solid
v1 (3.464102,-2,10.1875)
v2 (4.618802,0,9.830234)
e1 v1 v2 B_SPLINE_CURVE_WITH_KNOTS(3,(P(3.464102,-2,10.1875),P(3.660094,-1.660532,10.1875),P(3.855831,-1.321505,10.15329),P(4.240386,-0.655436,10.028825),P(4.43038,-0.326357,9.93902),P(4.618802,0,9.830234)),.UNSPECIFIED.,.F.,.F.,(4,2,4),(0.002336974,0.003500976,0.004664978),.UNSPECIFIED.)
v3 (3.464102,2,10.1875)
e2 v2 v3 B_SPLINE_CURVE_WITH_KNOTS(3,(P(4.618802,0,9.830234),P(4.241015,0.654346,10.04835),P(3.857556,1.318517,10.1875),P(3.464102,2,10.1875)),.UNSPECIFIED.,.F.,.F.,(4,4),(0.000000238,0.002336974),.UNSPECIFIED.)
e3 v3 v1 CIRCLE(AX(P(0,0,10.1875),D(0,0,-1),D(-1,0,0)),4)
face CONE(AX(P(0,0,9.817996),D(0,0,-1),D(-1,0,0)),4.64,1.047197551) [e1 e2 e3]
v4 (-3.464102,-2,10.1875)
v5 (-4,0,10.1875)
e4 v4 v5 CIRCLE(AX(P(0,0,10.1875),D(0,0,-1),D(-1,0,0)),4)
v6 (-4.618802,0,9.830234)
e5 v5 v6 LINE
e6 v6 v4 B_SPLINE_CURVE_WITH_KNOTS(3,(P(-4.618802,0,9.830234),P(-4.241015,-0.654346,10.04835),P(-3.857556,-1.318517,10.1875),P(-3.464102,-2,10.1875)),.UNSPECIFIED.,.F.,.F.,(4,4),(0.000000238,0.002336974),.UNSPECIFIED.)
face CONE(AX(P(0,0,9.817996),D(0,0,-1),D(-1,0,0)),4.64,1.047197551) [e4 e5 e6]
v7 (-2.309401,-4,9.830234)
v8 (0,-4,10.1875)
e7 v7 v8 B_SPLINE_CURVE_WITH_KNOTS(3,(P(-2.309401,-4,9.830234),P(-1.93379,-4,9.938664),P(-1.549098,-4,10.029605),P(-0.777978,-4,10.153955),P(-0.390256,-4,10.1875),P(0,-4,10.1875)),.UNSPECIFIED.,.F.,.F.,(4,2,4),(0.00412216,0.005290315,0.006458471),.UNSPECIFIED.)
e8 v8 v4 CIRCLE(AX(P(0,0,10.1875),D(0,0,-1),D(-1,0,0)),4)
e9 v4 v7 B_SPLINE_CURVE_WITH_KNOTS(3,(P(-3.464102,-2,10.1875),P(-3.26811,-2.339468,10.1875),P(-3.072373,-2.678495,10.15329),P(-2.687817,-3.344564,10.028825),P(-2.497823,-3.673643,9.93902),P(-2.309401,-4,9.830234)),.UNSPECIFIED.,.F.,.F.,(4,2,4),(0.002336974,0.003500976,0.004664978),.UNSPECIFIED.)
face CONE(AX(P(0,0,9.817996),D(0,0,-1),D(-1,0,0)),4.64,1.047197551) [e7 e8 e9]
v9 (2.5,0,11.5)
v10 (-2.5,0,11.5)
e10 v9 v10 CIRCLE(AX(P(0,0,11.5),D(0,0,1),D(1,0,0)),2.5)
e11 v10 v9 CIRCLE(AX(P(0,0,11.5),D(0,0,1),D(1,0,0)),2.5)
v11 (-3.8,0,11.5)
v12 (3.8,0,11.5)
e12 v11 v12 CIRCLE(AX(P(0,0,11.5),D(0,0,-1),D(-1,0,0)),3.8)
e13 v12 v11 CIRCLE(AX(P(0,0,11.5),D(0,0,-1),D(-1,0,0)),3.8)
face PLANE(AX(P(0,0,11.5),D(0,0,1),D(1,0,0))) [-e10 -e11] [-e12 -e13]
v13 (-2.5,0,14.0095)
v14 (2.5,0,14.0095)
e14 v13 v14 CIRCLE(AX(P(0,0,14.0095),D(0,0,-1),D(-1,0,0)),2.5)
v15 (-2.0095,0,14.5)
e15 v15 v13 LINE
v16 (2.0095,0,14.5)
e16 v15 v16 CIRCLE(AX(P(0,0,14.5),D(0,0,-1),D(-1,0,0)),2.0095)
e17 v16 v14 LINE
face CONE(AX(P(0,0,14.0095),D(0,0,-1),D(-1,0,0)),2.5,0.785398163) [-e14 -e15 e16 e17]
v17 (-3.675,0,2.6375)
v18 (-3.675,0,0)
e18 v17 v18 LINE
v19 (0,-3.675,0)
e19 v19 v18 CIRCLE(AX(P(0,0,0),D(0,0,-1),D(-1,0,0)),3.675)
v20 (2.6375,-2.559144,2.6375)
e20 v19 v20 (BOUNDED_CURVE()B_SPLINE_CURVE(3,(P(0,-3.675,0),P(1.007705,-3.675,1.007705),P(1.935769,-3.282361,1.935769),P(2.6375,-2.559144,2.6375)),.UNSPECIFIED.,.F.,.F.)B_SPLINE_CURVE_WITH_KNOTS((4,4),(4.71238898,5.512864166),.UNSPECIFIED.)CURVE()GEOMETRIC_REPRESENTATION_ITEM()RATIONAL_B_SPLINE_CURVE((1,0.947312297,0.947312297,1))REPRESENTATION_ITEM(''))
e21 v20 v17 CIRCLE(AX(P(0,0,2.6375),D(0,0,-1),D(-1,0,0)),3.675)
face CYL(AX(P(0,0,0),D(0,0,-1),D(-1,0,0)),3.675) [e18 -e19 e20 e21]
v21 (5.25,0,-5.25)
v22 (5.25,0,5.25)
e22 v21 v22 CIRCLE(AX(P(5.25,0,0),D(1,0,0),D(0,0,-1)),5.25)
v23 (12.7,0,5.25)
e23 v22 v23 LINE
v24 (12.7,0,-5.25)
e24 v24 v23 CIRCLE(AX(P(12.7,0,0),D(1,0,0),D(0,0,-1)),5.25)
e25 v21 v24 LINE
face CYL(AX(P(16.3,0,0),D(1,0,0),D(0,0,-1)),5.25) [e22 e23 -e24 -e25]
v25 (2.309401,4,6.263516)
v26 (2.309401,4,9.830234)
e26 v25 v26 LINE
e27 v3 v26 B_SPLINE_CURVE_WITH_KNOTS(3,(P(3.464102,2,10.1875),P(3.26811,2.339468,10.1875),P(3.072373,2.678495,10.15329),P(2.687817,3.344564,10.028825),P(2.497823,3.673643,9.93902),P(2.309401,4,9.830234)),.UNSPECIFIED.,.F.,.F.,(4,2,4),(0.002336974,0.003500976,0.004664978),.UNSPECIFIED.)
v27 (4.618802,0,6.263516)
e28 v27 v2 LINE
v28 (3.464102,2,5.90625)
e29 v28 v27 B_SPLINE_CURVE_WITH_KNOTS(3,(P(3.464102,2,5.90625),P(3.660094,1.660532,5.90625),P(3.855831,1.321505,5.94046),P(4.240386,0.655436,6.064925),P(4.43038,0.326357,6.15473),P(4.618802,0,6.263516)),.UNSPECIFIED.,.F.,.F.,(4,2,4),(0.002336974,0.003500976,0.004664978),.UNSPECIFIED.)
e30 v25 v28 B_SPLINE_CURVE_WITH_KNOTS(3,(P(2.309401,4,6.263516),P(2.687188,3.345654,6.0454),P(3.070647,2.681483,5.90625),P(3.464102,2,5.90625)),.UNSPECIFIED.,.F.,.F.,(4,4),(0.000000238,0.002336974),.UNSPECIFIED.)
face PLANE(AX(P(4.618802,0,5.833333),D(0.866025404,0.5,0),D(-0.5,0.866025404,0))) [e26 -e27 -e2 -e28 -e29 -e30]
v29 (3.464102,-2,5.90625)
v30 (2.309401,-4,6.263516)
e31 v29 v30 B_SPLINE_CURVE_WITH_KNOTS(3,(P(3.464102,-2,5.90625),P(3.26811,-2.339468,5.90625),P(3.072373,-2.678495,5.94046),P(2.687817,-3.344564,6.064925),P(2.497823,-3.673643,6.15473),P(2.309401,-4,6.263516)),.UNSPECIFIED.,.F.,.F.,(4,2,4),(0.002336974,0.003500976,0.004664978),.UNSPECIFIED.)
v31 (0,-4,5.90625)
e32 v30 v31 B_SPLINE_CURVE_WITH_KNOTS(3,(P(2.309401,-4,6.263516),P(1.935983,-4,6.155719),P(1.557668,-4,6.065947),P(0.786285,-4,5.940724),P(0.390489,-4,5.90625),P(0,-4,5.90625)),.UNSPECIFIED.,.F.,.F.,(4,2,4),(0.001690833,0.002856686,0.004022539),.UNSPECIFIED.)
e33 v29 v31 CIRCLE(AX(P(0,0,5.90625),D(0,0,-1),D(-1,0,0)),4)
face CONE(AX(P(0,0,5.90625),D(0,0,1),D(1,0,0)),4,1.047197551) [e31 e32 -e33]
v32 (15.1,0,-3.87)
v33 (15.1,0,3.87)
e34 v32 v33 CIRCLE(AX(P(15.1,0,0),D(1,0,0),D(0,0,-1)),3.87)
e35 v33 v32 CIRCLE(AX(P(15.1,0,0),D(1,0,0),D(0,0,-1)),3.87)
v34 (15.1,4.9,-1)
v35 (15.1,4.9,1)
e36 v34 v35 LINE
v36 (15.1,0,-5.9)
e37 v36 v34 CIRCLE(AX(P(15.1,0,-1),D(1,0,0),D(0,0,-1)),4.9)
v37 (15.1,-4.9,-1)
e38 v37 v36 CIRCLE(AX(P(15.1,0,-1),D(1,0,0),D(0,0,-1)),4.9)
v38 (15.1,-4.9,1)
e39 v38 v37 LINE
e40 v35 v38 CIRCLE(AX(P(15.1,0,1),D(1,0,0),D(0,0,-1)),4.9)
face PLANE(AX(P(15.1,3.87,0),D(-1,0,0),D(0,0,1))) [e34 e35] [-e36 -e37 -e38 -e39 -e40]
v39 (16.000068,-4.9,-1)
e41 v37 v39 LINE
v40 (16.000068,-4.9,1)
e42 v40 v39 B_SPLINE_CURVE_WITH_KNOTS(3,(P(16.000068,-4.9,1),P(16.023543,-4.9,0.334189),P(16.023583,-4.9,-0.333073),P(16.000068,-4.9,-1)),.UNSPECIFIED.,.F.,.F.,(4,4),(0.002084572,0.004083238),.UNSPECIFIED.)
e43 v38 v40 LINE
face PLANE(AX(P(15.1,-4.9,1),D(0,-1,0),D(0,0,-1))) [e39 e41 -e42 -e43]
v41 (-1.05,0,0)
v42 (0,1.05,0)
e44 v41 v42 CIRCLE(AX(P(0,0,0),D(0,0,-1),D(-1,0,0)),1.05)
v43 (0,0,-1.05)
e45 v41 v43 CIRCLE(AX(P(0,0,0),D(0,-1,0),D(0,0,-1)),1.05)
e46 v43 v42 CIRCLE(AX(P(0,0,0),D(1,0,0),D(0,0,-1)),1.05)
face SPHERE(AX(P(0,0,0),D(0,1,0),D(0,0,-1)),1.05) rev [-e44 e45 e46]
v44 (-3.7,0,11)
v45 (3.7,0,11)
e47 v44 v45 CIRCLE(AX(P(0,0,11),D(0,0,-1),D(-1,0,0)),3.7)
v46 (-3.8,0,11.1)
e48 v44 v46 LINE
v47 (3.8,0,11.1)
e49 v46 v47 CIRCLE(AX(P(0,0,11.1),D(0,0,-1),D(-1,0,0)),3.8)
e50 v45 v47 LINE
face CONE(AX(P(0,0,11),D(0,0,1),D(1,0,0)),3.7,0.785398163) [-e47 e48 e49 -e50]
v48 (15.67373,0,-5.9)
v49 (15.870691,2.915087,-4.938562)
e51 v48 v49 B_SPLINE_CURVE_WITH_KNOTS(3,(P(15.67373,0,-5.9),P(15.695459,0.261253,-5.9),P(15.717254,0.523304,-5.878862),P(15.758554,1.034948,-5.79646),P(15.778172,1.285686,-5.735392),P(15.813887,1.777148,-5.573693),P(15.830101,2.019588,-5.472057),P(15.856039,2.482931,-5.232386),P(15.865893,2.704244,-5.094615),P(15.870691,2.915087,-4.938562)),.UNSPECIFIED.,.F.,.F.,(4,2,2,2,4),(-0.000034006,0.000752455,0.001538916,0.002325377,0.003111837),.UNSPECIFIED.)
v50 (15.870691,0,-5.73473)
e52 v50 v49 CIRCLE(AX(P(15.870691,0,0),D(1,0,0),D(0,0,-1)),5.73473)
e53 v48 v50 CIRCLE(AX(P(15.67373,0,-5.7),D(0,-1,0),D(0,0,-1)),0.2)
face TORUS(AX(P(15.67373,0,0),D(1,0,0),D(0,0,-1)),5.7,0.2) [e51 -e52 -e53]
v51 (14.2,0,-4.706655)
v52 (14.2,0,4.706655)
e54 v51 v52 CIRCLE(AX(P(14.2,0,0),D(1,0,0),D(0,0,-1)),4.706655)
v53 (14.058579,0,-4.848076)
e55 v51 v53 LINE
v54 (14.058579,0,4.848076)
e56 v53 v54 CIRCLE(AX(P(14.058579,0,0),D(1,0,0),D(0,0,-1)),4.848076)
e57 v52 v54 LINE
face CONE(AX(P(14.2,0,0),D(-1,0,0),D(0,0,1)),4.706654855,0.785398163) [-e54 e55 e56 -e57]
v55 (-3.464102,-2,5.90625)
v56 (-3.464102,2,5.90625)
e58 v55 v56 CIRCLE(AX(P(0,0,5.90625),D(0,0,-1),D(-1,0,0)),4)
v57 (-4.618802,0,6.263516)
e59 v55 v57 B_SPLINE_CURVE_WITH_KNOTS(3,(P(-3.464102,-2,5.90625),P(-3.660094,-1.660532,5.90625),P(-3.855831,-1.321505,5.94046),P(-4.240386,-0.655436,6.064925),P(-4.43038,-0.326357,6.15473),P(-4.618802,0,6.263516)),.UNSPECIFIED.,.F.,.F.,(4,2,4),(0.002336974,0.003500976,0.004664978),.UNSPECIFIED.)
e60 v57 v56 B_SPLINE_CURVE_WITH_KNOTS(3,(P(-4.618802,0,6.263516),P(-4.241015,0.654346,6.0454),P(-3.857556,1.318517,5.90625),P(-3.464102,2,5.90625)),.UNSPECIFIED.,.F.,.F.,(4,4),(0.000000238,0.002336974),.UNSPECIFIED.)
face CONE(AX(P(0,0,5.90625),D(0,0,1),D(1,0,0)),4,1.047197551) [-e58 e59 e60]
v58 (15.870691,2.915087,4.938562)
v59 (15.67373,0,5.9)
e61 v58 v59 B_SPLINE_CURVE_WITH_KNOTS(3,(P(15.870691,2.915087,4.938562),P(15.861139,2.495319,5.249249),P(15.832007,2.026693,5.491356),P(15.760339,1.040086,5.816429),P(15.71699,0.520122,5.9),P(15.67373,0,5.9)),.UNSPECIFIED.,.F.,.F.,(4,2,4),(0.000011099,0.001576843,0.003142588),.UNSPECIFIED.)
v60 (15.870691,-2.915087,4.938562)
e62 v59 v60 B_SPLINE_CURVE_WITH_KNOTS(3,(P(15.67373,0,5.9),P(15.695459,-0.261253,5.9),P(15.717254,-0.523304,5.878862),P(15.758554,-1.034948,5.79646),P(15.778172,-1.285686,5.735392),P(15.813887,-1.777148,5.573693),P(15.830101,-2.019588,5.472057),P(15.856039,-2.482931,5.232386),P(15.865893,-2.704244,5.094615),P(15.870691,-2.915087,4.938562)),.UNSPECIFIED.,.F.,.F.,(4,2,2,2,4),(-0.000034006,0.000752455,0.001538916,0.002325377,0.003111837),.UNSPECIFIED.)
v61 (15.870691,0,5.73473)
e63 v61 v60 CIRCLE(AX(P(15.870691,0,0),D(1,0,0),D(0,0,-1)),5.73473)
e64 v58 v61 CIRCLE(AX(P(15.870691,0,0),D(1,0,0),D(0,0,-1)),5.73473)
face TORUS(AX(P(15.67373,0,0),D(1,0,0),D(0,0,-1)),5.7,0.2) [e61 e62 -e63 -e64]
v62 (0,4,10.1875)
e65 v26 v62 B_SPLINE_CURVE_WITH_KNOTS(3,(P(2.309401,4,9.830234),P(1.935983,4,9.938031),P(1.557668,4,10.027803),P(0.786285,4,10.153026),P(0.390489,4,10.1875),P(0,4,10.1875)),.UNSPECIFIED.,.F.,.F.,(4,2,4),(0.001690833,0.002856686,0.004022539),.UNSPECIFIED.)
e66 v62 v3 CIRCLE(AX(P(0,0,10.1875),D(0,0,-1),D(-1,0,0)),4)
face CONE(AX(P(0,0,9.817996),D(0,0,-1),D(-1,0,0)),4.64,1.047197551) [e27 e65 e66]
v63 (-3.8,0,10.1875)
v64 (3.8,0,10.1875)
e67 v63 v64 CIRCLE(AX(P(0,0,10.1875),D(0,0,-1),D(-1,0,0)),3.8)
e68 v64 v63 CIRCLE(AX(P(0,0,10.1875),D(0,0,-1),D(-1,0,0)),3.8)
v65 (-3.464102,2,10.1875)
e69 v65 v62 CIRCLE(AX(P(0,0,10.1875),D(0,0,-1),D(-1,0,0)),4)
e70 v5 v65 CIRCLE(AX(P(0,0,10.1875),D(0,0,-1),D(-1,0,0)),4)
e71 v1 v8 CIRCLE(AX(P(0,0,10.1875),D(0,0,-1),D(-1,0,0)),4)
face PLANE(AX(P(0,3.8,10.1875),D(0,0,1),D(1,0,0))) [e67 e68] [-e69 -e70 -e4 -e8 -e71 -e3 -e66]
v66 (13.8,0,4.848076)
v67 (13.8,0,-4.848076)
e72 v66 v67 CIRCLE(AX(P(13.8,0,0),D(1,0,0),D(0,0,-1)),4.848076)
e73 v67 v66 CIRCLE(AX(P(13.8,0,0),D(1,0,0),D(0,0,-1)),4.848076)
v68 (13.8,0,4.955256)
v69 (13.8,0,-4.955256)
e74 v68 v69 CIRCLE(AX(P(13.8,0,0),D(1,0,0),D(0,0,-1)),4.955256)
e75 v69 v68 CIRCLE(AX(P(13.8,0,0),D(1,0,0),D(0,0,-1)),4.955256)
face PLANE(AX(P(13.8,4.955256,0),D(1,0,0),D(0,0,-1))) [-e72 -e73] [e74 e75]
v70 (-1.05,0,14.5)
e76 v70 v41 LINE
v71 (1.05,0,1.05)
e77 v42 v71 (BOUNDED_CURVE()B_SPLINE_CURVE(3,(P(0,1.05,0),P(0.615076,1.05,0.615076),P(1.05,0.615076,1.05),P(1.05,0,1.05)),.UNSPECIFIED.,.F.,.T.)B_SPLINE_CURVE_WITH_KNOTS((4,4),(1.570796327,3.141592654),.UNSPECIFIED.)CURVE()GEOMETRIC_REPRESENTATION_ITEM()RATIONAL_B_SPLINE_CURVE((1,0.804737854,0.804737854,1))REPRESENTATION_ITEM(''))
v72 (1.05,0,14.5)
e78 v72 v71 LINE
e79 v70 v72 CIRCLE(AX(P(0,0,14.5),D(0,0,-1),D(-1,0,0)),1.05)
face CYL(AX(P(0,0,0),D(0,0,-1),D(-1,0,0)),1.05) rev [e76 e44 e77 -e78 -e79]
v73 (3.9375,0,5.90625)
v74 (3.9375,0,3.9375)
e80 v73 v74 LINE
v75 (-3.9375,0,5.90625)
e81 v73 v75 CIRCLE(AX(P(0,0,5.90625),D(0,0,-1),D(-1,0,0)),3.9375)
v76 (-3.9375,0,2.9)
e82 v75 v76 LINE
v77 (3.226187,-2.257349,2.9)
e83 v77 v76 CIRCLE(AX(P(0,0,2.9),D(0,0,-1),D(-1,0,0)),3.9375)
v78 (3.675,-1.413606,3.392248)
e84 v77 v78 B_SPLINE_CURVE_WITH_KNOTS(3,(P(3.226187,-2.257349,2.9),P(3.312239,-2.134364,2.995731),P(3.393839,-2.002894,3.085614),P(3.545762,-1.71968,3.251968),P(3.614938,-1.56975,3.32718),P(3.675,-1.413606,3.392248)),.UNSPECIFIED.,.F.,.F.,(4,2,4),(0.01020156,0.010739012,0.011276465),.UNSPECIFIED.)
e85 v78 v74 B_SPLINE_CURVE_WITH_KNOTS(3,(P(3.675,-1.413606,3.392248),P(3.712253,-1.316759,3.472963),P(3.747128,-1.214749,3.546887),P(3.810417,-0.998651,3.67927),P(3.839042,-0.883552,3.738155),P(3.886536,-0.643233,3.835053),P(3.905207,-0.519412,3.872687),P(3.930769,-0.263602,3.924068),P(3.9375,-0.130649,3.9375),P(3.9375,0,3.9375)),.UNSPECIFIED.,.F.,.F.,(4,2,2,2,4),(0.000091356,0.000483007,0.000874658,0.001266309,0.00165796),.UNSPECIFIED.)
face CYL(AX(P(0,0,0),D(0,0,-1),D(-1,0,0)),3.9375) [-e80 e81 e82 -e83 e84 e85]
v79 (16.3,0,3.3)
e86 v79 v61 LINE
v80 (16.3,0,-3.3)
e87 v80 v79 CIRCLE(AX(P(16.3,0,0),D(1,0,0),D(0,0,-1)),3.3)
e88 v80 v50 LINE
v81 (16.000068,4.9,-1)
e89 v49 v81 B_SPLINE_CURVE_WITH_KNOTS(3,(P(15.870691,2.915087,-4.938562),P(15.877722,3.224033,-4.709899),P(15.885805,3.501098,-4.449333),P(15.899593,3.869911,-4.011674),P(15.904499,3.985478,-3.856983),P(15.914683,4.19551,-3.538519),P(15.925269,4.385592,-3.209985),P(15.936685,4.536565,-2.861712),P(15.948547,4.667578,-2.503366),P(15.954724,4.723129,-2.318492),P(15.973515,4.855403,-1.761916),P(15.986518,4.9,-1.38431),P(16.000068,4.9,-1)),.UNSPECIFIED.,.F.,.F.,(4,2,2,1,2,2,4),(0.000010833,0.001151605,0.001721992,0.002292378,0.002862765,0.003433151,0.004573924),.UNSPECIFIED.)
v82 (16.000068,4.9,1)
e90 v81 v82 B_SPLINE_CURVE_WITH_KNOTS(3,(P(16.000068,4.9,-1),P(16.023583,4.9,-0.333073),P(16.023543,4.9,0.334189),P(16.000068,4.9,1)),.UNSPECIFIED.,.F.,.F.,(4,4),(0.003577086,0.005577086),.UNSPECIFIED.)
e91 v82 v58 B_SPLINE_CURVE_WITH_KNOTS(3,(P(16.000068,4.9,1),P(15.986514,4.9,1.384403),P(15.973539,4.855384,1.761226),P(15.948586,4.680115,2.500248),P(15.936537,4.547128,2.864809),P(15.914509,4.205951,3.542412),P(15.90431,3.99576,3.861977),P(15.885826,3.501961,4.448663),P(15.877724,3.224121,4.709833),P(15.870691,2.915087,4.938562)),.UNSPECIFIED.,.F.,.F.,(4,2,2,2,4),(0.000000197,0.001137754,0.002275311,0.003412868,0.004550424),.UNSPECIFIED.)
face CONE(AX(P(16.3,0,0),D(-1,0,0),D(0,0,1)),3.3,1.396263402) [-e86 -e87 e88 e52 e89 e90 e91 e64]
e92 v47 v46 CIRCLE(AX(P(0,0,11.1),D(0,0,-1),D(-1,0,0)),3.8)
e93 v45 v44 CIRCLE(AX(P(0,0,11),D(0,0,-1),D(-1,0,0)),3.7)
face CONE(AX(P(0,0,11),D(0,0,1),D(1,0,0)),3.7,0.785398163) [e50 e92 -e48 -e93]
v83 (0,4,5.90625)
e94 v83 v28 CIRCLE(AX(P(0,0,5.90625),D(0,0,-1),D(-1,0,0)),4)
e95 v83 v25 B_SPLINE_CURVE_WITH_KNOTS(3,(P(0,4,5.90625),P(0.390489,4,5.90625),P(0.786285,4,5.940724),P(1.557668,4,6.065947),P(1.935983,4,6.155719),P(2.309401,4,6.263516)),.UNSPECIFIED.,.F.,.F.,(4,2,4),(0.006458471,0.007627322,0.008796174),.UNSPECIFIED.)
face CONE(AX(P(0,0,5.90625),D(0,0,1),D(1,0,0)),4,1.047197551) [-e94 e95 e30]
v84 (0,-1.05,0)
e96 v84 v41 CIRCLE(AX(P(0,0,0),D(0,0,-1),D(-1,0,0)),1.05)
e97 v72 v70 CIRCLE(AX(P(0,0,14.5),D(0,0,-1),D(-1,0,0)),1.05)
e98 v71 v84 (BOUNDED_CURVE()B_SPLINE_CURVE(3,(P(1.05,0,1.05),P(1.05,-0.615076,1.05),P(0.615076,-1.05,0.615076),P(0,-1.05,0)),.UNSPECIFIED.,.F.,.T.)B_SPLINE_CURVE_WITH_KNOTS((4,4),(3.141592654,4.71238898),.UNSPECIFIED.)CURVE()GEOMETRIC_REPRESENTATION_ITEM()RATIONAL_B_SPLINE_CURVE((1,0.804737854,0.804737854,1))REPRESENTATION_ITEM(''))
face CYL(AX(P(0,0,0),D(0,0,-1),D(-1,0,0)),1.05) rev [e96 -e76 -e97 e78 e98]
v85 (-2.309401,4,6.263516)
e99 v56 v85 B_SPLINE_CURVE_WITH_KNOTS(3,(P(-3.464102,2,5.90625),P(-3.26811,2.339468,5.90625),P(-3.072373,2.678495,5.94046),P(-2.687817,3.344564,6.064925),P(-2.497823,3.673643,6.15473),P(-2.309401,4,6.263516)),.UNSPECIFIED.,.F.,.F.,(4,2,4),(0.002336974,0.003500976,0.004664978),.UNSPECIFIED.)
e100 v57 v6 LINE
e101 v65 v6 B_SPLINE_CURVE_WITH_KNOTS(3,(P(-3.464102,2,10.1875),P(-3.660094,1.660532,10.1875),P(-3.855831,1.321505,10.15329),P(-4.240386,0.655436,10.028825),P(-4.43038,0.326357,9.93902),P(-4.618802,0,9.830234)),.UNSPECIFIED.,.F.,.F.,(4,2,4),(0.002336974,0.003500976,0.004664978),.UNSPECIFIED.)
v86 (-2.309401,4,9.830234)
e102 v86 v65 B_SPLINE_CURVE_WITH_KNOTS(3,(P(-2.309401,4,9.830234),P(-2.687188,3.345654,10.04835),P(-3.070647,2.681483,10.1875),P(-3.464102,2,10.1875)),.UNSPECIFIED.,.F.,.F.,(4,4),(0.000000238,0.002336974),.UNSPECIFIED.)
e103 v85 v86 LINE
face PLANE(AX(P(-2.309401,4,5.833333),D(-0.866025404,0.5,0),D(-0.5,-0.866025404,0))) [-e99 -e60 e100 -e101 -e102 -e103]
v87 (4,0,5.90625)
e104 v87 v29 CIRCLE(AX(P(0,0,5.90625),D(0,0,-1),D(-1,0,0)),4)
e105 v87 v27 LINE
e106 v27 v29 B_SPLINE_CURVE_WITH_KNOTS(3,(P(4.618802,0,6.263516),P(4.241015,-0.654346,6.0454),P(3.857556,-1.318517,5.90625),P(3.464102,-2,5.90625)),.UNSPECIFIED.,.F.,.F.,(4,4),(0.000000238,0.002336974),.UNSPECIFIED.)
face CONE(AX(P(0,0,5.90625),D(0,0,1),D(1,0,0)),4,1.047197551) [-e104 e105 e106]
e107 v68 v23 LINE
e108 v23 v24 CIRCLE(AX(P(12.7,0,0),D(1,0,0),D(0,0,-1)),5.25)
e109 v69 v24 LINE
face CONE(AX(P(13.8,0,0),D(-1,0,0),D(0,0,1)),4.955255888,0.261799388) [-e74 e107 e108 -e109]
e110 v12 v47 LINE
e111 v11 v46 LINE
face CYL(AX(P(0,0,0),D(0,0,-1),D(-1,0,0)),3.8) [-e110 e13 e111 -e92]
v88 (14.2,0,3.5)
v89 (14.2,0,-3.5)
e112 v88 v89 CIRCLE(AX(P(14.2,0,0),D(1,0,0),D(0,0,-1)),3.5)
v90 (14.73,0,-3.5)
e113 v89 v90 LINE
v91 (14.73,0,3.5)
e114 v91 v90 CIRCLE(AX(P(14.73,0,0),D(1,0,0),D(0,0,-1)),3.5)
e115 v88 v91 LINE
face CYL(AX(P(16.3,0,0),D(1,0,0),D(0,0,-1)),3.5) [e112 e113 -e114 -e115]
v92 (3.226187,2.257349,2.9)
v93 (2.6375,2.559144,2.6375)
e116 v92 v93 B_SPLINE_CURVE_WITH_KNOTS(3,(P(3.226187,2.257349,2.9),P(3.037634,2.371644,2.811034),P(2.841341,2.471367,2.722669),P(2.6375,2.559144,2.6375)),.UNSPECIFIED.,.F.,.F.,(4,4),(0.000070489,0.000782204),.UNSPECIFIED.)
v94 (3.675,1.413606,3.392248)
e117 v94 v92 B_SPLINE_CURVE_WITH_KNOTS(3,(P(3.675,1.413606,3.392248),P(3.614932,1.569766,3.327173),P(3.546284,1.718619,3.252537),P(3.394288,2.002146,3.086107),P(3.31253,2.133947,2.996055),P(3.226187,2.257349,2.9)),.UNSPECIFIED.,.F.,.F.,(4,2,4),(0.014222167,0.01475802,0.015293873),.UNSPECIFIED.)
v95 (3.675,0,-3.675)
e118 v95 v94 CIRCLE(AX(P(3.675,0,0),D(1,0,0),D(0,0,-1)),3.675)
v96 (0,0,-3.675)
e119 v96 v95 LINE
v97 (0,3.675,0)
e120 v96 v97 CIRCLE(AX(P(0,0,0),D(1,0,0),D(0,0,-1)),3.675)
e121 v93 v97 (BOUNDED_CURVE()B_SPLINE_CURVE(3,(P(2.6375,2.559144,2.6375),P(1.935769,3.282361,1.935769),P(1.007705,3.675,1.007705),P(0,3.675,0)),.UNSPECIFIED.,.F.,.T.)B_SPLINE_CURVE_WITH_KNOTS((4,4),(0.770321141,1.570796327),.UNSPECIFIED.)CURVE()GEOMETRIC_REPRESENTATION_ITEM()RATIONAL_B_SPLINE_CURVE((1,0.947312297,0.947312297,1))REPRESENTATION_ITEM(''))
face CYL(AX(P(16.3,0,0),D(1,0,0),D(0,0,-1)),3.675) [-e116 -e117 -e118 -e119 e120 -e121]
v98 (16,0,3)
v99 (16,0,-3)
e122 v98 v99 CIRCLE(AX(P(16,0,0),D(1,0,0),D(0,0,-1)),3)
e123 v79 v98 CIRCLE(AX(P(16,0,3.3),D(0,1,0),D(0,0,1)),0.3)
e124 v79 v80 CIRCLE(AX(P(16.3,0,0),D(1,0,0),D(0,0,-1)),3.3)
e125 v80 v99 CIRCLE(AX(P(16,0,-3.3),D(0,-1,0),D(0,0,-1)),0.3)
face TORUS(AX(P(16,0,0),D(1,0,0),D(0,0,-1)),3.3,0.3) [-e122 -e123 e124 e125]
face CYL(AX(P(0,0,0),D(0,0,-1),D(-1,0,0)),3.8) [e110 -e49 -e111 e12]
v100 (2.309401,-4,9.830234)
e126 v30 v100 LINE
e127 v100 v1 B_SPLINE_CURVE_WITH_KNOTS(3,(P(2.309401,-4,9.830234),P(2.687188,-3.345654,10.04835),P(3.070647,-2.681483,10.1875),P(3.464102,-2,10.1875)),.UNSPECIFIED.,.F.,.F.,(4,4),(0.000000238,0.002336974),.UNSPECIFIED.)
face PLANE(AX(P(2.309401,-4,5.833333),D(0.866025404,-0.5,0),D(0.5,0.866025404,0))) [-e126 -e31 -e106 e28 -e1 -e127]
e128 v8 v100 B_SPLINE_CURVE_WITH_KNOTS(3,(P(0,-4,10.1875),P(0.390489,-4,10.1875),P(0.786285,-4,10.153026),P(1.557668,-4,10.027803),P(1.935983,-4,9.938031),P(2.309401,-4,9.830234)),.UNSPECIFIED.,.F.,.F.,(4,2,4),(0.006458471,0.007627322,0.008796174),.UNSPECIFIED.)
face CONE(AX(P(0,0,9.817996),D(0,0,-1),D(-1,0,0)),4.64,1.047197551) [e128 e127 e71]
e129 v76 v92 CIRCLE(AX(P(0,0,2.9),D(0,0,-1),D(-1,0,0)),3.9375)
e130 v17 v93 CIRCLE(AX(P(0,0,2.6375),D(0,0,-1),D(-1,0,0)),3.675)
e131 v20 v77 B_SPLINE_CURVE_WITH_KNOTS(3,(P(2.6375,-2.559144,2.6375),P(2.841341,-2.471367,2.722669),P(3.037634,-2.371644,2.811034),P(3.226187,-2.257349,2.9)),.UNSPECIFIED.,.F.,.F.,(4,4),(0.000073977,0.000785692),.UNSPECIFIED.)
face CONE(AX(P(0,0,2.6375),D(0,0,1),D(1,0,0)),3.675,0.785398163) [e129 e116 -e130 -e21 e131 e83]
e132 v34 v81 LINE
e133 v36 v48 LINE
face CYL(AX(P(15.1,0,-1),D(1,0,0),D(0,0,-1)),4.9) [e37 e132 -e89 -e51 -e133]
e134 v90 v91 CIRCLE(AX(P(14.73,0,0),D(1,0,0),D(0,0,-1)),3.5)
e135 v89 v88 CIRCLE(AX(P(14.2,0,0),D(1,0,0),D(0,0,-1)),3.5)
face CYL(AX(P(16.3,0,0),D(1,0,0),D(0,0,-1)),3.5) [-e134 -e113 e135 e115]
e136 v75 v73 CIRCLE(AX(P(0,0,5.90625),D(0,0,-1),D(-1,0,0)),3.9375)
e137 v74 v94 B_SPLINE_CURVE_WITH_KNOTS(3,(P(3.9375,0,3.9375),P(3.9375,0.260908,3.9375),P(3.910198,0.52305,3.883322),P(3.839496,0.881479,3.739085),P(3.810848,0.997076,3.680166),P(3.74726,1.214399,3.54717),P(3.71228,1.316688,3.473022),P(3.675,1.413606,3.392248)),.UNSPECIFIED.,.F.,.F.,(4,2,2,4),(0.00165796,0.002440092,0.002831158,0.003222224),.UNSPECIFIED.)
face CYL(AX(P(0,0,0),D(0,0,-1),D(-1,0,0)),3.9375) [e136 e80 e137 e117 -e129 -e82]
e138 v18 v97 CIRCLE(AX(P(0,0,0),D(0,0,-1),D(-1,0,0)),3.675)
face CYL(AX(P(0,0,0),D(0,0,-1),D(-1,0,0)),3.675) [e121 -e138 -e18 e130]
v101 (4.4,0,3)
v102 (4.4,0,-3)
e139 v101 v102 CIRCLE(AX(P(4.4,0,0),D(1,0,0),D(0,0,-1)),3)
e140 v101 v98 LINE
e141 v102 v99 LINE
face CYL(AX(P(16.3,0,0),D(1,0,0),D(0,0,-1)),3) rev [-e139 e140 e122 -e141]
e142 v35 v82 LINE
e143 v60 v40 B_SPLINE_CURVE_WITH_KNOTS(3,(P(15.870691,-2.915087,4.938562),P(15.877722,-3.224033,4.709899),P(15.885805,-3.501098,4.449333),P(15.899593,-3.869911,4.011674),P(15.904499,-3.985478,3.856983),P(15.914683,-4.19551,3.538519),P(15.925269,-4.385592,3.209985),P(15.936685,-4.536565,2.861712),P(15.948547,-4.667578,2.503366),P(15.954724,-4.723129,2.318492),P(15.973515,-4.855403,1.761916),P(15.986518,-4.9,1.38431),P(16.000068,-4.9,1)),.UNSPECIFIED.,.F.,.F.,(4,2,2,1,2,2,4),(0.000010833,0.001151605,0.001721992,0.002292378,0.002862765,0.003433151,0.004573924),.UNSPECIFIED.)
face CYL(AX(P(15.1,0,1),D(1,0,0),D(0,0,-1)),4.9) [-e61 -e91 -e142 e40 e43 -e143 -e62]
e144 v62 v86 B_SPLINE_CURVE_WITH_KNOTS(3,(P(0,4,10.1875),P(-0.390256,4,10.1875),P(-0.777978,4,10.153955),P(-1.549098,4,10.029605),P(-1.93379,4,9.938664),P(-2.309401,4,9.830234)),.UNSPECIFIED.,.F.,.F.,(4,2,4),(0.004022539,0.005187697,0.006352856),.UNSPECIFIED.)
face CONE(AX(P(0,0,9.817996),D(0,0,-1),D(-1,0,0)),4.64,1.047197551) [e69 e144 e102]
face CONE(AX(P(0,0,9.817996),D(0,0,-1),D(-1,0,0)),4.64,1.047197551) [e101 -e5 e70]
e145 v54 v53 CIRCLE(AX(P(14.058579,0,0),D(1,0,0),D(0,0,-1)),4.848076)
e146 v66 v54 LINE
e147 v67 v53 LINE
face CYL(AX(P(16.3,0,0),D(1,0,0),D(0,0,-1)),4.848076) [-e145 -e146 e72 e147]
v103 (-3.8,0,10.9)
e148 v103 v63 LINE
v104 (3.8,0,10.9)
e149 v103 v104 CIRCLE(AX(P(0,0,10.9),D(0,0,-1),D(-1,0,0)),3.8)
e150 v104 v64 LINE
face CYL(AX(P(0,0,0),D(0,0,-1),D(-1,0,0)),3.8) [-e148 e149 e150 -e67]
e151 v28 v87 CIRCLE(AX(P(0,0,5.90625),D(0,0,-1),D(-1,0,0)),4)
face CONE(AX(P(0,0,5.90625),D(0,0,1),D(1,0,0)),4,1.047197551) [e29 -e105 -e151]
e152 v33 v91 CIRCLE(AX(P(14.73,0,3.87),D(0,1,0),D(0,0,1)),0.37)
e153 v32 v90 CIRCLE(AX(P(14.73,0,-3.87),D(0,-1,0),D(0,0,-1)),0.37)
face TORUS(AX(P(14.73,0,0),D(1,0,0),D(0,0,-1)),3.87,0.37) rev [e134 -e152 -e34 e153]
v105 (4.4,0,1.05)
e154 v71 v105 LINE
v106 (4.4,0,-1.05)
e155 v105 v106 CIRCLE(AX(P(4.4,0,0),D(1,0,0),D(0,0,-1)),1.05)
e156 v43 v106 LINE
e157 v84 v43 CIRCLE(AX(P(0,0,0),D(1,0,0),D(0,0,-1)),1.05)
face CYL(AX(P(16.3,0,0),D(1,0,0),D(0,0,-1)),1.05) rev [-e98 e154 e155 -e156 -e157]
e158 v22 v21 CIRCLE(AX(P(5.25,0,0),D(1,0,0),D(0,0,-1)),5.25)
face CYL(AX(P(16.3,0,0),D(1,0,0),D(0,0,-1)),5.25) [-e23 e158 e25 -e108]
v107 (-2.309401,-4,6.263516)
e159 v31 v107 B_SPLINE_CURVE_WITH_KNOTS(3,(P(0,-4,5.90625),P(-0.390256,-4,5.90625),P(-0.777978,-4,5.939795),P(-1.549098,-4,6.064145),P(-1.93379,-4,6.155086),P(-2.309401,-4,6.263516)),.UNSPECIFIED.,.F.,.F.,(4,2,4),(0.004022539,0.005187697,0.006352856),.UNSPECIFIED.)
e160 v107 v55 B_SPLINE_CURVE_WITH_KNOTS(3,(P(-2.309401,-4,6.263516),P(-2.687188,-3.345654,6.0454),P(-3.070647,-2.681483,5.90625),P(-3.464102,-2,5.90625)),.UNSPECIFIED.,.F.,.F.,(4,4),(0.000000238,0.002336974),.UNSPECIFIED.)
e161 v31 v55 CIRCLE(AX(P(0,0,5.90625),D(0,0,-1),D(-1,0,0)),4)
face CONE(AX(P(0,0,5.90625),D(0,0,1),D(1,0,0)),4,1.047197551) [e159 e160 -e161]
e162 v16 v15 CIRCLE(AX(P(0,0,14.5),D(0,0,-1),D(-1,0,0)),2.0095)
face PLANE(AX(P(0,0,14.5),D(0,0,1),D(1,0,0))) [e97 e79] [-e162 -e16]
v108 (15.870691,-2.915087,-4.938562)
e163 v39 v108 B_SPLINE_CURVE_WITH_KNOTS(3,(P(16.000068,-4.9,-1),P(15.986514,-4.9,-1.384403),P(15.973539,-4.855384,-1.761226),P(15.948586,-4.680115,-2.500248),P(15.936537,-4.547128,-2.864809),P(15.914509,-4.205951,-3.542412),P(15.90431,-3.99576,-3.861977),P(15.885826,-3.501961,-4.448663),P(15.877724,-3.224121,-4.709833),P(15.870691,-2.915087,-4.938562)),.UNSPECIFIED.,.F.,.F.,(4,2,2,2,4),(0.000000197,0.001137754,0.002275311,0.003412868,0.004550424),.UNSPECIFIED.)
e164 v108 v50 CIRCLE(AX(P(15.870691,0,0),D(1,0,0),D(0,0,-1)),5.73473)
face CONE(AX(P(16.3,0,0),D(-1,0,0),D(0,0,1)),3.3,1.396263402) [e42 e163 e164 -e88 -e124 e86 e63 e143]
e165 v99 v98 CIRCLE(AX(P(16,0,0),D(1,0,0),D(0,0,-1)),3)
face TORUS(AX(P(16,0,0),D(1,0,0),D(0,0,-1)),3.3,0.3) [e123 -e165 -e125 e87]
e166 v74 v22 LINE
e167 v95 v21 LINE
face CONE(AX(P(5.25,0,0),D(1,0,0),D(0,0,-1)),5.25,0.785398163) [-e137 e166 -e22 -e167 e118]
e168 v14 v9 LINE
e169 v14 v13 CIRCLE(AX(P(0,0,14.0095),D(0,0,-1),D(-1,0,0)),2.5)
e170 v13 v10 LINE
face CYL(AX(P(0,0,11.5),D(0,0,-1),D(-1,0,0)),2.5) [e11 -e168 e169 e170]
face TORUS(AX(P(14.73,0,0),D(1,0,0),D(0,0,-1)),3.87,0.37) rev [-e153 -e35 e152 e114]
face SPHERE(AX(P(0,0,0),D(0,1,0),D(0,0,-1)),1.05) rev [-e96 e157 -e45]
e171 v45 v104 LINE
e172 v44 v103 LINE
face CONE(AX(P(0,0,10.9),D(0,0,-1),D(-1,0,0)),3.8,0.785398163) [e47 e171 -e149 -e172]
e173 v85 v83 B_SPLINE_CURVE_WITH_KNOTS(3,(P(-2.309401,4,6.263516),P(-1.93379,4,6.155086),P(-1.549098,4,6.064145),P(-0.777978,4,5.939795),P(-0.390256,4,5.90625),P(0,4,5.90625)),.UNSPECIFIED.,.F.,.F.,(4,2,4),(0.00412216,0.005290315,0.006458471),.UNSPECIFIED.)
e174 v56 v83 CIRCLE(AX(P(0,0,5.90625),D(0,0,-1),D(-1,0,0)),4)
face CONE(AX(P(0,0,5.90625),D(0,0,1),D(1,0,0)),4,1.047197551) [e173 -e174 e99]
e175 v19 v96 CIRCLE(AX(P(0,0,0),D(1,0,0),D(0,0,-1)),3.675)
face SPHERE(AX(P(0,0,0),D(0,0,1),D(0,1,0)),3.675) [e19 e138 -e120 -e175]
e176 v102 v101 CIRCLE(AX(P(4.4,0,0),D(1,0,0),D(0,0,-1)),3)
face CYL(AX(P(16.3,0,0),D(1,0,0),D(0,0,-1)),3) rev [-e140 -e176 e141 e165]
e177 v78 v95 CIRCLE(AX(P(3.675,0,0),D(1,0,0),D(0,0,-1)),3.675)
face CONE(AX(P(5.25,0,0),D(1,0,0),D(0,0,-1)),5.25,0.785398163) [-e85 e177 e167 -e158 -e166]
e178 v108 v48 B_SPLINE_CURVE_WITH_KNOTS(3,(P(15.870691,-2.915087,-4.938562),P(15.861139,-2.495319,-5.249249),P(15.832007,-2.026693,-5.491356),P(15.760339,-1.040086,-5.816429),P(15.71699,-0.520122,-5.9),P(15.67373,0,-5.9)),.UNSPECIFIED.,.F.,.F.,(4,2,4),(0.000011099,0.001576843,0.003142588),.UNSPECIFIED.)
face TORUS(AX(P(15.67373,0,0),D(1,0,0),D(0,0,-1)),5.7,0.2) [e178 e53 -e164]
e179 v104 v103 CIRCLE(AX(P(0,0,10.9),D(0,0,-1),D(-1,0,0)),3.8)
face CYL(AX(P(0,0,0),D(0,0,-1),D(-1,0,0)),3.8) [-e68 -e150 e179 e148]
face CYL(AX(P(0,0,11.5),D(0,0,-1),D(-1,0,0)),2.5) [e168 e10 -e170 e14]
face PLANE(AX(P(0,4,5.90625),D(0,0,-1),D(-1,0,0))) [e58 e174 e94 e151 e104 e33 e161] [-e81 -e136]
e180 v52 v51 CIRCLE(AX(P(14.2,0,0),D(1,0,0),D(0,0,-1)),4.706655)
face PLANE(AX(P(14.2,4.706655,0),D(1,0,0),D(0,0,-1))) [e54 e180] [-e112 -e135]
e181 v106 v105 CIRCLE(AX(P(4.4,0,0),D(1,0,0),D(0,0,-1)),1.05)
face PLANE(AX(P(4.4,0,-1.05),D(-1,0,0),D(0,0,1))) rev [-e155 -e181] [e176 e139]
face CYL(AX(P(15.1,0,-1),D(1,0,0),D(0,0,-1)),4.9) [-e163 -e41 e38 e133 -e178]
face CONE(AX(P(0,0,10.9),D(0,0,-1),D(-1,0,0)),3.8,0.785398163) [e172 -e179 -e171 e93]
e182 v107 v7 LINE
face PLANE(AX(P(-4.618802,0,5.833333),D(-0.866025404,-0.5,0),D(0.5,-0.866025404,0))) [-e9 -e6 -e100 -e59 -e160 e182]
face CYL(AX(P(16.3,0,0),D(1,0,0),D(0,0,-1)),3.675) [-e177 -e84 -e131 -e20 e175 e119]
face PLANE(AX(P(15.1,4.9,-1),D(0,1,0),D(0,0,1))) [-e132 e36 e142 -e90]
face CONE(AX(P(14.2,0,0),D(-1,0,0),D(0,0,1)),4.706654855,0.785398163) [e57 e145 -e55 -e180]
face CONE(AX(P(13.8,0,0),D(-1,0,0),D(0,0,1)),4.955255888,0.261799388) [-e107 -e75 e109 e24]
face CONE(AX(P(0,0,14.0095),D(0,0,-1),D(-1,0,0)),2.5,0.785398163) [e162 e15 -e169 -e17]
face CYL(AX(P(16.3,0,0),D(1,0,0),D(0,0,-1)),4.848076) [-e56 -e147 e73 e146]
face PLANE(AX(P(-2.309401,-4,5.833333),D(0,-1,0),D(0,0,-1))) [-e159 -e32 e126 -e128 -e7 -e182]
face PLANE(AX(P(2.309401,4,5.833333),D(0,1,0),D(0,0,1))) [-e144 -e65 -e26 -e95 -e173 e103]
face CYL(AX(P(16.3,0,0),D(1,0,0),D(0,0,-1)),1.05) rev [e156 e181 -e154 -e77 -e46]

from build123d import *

# Parameters (mm, degrees)
CUT_EXTRUDE1_DEPTH = 1.2
SKETCH6_W          = 14.5
SKETCH6_H          = 1.05
SKETCH7_W          = 16
SKETCH7_H          = 16
CUT_EXTRUDE2_DEPTH = 5.666666667


with BuildPart() as part:
    # Sketch1 → Revolve1 (revolve)
    with BuildSketch(Plane.XY, mode=Mode.PRIVATE) as revolve1_sk:
        with BuildLine():
            Line((0, 3.675), (3.675, 3.675))
            Line((3.675, 3.675), (5.25, 5.25))
            Line((5.25, 5.25), (12.7, 5.25))
            Line((12.7, 5.25), (13.8, 4.955255888))
            Line((13.8, 4.955255888), (13.8, 4.848076211))
            Line((13.8, 4.848076211), (14.058578644, 4.848076211))
            Line((14.058578644, 4.848076211), (14.2, 4.706654855))
            Line((14.2, 4.706654855), (14.2, 3.5))
            Line((14.2, 3.5), (14.73, 3.5))
            ThreePointArc((14.73, 3.5), (14.991629509, 3.608370491), (15.1, 3.87))
            Line((15.1, 3.87), (15.1, 5.9))
            Line((15.1, 5.9), (15.673729924, 5.9))
            ThreePointArc((15.673729924, 5.9), (15.802287446, 5.853208889), (15.870691475, 5.734729636))
            Line((15.870691475, 5.734729636), (16.3, 3.3))
            Line((16.3, 3.3), (16.3, 0))
            Line((16.3, 0), (-3.675, 0))
            ThreePointArc((-3.675, 0), (-2.598617421, 2.598617421), (0, 3.675))
        make_face()
    revolve(revolve1_sk.sketch.rotate(Axis((16.3, 0, 0), (-1, 0, 0)), 90), axis=Axis((16.3, 0, 0), (-1, 0, 0)))

    # Sketch2 → Revolve2 (revolve)
    with BuildSketch(Plane(origin=(0, 0, 0), x_dir=(0, 0, -1), z_dir=(1, 0, 0)), mode=Mode.PRIVATE) as revolve2_sk:
        Polygon((-11.5, 0), (-11.5, 3.8), (-11.1, 3.8), (-11, 3.7), (-10.9, 3.8), (-10.1875, 3.8), (-10.1875, 4), (-9.817995828, 4.64), (-6.275754172, 4.64), (-5.90625, 4), (-5.90625, 3.9375), (-2.9, 3.9375), (-2.6375, 3.675), (0, 3.675), (0, 0), align=None)
    revolve(revolve2_sk.sketch.rotate(Axis((0, 0, 0), (0, 0, 1)), 90), axis=Axis((0, 0, 0), (0, 0, 1)))

    # Sketch3 → Revolve3 (revolve)
    with BuildSketch(Plane(origin=(0, 0, 0), x_dir=(0, 0, -1), z_dir=(1, 0, 0)), mode=Mode.PRIVATE) as revolve3_sk:
        Polygon((-14.5, 0), (-14.5, 2.0095), (-14.0095, 2.5), (-11.5, 2.5), (-11.5, 0), align=None)
    revolve(revolve3_sk.sketch.rotate(Axis((0, 0, 11.5), (0, 0, 1)), 90), axis=Axis((0, 0, 11.5), (0, 0, 1)))

    # Sketch4 → Cut-Extrude1 (cut)
    with BuildSketch(Plane(origin=(16.3, 0, 0), x_dir=(0, 0, -1), z_dir=(1, 0, 0))):
        Polygon((-7.08, 4.087639906), (-7.08, -4.087639906), (0, -8.175279812), (7.08, -4.087639906), (7.08, 4.087639906), (0, 8.175279812), align=None)
        with BuildLine():
            Line((-1, -4.9), (1, -4.9))
            ThreePointArc((1, -4.9), (5.9, 0), (1, 4.9))
            Line((1, 4.9), (-1, 4.9))
            ThreePointArc((-1, 4.9), (-5.9, 0), (-1, -4.9))
        make_face(mode=Mode.SUBTRACT)
    extrude(amount=-CUT_EXTRUDE1_DEPTH, mode=Mode.SUBTRACT)

    # Sketch6 → Cut-Revolve1 (revolve, cut)
    with BuildSketch(Plane(origin=(0, 0, 0), x_dir=(0, 0, -1), z_dir=(1, 0, 0)), mode=Mode.PRIVATE) as cut_revolve1_sk:
        with Locations((-7.25, 0.525)):
            Rectangle(SKETCH6_W, SKETCH6_H)
    revolve(cut_revolve1_sk.sketch.rotate(Axis((0, 0, 0), (0, 0, 1)), 90), axis=Axis((0, 0, 0), (0, 0, 1)), mode=Mode.SUBTRACT)

    # Sketch5 → Cut-Revolve2 (revolve, cut)
    with BuildSketch(Plane(origin=(0, 0, 0), x_dir=(1, 0, 0), z_dir=(0, 1, 0))):
        with BuildLine():
            Line((0, 1.05), (4.4, 1.05))
            Line((4.4, 1.05), (4.4, 3))
            Line((4.4, 3), (16, 3))
            ThreePointArc((16, 3), (16.212132034, 3.087867966), (16.3, 3.3))
            Line((16.3, 3.3), (16.3, 0))
            Line((16.3, 0), (-1.05, 0))
            ThreePointArc((-1.05, 0), (-0.74246212, 0.74246212), (0, 1.05))
        make_face()
    revolve(axis=Axis((16.3, 0, 0), (-1, 0, 0)), mode=Mode.SUBTRACT)

    # Sketch7 → Cut-Extrude2 (cut)
    with BuildSketch(Plane.XY.offset(11.5)):
        Rectangle(SKETCH7_W, SKETCH7_H)
        Polygon((-4.618802154, 0), (-2.309401077, -4), (2.309401077, -4), (4.618802154, 0), (2.309401077, 4), (-2.309401077, 4), align=None, mode=Mode.SUBTRACT)
    extrude(amount=-CUT_EXTRUDE2_DEPTH, mode=Mode.SUBTRACT)


solid = part.part
